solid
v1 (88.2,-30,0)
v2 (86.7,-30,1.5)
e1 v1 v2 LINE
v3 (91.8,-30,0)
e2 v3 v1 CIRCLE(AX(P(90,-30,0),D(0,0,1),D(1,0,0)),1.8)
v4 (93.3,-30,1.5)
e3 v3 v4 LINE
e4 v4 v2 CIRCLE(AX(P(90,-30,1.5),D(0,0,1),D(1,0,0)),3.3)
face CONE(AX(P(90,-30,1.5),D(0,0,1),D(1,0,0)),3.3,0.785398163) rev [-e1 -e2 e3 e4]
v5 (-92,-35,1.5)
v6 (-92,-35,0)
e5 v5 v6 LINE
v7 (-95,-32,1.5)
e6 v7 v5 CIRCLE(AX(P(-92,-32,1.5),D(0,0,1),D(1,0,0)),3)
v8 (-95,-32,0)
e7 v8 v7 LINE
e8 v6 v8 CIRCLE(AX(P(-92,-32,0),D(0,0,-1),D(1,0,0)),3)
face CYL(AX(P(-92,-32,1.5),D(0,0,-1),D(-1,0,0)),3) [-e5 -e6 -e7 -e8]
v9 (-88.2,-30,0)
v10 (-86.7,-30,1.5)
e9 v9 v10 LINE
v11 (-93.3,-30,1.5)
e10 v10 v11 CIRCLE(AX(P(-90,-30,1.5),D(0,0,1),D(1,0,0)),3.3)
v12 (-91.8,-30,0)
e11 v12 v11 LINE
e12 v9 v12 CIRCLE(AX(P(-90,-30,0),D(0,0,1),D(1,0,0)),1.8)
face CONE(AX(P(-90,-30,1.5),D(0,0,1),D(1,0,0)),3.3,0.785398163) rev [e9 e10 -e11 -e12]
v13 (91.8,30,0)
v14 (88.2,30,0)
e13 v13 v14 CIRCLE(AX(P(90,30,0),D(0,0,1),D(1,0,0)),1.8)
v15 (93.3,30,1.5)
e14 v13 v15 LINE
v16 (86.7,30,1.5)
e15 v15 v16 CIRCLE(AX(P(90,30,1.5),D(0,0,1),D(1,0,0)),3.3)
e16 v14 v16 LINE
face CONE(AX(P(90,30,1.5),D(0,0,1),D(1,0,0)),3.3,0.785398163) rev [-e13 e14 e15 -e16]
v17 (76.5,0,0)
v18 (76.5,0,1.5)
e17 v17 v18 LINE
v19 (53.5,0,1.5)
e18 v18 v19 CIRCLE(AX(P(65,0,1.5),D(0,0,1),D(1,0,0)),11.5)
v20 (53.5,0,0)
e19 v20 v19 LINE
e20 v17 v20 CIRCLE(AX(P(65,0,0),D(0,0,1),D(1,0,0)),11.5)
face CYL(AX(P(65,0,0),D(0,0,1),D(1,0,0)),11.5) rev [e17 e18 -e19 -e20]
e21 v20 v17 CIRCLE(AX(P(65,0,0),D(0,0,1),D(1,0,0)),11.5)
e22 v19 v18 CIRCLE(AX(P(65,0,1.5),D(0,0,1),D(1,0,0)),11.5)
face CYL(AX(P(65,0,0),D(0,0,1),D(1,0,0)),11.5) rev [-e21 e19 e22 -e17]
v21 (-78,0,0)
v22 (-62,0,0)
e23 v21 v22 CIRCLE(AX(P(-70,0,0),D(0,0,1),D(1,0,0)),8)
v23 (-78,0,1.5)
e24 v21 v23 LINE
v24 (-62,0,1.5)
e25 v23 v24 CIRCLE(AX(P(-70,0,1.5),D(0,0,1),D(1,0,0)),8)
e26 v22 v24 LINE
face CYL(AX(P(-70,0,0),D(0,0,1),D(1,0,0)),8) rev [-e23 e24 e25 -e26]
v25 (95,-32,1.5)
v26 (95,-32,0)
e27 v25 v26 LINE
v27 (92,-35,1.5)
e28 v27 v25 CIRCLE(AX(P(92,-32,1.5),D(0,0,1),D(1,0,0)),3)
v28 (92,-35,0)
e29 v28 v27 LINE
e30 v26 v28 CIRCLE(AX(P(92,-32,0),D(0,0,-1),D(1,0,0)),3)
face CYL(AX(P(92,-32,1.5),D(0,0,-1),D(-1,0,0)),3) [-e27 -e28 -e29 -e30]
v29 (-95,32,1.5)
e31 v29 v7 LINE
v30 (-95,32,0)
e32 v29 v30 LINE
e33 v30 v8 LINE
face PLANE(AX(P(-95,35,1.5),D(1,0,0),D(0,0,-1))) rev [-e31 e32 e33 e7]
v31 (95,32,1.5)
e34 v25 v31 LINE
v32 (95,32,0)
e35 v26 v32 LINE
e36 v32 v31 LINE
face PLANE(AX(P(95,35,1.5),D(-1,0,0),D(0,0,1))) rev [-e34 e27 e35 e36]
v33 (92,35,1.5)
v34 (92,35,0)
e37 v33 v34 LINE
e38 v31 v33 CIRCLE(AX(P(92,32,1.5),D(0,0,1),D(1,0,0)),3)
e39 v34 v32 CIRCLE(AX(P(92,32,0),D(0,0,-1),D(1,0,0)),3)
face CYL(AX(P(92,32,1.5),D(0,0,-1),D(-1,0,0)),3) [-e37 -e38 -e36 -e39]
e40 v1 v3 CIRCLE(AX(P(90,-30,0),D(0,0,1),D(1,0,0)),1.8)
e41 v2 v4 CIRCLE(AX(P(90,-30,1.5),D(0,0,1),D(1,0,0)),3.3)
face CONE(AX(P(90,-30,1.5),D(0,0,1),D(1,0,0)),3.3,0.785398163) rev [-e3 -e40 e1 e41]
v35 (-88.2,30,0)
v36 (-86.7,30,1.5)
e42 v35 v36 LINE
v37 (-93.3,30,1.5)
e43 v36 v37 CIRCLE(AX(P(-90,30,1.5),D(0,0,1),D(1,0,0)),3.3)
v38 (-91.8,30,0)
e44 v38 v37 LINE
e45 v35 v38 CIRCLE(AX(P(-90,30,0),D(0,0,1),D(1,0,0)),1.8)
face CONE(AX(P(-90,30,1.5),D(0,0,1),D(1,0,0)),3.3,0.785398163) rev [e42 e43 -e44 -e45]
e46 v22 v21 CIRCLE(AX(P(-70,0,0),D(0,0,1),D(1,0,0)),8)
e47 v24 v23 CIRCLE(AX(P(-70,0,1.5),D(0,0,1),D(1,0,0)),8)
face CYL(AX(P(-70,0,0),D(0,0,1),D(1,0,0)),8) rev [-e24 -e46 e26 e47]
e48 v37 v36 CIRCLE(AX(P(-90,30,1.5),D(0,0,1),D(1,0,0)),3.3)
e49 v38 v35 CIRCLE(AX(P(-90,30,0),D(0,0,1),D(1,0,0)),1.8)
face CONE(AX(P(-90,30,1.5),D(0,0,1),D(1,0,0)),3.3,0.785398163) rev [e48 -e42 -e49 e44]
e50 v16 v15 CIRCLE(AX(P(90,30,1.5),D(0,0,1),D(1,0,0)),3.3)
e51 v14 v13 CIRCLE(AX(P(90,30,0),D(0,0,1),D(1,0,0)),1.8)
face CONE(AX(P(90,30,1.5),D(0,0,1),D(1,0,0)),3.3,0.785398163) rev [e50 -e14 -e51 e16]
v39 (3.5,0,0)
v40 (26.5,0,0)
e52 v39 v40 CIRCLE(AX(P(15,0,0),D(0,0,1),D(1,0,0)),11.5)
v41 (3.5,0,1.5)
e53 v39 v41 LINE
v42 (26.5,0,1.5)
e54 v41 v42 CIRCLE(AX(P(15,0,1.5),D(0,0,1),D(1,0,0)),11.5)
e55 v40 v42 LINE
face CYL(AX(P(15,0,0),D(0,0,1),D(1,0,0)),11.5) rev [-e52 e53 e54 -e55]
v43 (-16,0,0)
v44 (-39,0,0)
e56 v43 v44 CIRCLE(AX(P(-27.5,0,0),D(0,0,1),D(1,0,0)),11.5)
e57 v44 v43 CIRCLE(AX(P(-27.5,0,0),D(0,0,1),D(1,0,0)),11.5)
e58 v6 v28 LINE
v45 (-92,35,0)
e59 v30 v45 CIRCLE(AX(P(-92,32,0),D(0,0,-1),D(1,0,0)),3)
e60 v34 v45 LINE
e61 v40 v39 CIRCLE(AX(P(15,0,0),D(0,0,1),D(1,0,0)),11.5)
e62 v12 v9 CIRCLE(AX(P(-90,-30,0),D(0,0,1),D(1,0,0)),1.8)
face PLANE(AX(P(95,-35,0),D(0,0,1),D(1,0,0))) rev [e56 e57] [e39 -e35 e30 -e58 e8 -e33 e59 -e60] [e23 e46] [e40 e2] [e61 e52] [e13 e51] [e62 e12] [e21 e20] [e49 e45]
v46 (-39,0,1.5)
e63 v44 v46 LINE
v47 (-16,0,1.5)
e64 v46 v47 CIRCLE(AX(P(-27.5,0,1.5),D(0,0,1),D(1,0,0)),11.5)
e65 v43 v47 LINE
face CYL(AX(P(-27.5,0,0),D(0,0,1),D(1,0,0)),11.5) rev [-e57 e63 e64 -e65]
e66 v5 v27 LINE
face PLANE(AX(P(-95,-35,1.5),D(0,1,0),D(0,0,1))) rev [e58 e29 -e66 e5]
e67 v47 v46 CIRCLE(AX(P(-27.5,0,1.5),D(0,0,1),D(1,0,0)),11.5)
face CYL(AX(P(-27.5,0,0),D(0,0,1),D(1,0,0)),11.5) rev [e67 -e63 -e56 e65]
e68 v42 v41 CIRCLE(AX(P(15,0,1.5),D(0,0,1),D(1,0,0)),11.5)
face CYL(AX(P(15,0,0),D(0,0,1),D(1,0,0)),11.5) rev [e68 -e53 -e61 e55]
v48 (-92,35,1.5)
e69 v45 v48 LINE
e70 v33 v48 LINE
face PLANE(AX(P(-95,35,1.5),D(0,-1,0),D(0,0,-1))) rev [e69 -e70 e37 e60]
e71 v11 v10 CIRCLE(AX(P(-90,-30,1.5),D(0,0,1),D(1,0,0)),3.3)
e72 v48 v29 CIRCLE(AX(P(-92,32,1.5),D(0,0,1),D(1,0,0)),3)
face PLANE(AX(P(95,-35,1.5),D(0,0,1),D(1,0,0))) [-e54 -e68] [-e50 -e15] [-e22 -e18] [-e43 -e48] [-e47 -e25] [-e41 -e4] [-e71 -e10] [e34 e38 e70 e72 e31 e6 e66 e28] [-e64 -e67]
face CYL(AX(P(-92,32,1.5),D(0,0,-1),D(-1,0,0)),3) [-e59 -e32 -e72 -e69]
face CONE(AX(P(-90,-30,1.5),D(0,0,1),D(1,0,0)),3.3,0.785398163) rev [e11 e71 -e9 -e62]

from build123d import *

# Parameters (mm, degrees)
SKETCH_1_W               = 190
SKETCH_1_H               = 70
EXTRUDE_1_DEPTH          = 1.5
FILLET_1_R               = 3
SKETCH_2_R               = 11.5
SKETCH_2_R_2             = 8
CUT_EXTRUDE_1_DEPTH      = 1.5
HOLE_WIZARD_1_AT_2_COUNT = 2
HOLE_WIZARD_1_AT_2_PITCH = 60
HOLE_WIZARD_1_AT_3_COUNT = 2
HOLE_WIZARD_1_AT_3_PITCH = 189.73665961
HOLE_WIZARD_1_AT_4_COUNT = 2
HOLE_WIZARD_1_AT_4_PITCH = 180


with BuildPart() as part:
    # 草图1 → 凸台-拉伸1 (new body)
    with BuildSketch(Plane.XY):
        Rectangle(SKETCH_1_W, SKETCH_1_H)
    extrude(amount=EXTRUDE_1_DEPTH)

    # 圆角1
    fillet_1_edges = [part.edges().sort_by_distance(p)[0] for p in [
        (95, -35, 0.75),
        (-95, -35, 0.75),
        (-95, 35, 0.75),
        (95, 35, 0.75),
    ]]
    fillet(fillet_1_edges, radius=FILLET_1_R)

    # 草图2 → 切除-拉伸1 (cut)
    with BuildSketch(Plane.XY.offset(1.5)):
        with Locations((15, 0)):
            Circle(SKETCH_2_R)
        with Locations((-27.5, 0)):
            Circle(SKETCH_2_R)
        with Locations((65, 0)):
            Circle(SKETCH_2_R)
        with Locations((-70, 0)):
            Circle(SKETCH_2_R_2)
    extrude(amount=-CUT_EXTRUDE_1_DEPTH, mode=Mode.SUBTRACT)

    # 草图4 → 打孔尺寸根据十字槽半沉头木螺钉的类型1 (revolve, cut)
    with BuildSketch(Plane(origin=(-90, 30, 1.5), x_dir=(0, -1, 0), z_dir=(1, 0, 0))):
        Polygon((0, 0), (0, 1.5), (1.7, 1.5), (1.7, 1.6), (3.3, 0), align=None)
    hole_wizard_1 = revolve(axis=Axis((-90, 30, 7.85), (0, 0, -1)), mode=Mode.SUBTRACT)

    # 打孔尺寸根据十字槽半沉头木螺钉的类型1 at 2: 打孔尺寸根据十字槽半沉头木螺钉的类型1 ×2
    with Locations(*[(0, -i * HOLE_WIZARD_1_AT_2_PITCH, 0) for i in range(1, HOLE_WIZARD_1_AT_2_COUNT)]):
        add(hole_wizard_1, mode=Mode.SUBTRACT)

    # 打孔尺寸根据十字槽半沉头木螺钉的类型1 at 3: 打孔尺寸根据十字槽半沉头木螺钉的类型1 ×2
    with Locations(*[Vector(0.9486832980505139, -0.3162277660168379, 0) * (i * HOLE_WIZARD_1_AT_3_PITCH) for i in range(1, HOLE_WIZARD_1_AT_3_COUNT)]):
        add(hole_wizard_1, mode=Mode.SUBTRACT)

    # 打孔尺寸根据十字槽半沉头木螺钉的类型1 at 4: 打孔尺寸根据十字槽半沉头木螺钉的类型1 ×2
    with Locations(*[(i * HOLE_WIZARD_1_AT_4_PITCH, 0, 0) for i in range(1, HOLE_WIZARD_1_AT_4_COUNT)]):
        add(hole_wizard_1, mode=Mode.SUBTRACT)


solid = part.part
